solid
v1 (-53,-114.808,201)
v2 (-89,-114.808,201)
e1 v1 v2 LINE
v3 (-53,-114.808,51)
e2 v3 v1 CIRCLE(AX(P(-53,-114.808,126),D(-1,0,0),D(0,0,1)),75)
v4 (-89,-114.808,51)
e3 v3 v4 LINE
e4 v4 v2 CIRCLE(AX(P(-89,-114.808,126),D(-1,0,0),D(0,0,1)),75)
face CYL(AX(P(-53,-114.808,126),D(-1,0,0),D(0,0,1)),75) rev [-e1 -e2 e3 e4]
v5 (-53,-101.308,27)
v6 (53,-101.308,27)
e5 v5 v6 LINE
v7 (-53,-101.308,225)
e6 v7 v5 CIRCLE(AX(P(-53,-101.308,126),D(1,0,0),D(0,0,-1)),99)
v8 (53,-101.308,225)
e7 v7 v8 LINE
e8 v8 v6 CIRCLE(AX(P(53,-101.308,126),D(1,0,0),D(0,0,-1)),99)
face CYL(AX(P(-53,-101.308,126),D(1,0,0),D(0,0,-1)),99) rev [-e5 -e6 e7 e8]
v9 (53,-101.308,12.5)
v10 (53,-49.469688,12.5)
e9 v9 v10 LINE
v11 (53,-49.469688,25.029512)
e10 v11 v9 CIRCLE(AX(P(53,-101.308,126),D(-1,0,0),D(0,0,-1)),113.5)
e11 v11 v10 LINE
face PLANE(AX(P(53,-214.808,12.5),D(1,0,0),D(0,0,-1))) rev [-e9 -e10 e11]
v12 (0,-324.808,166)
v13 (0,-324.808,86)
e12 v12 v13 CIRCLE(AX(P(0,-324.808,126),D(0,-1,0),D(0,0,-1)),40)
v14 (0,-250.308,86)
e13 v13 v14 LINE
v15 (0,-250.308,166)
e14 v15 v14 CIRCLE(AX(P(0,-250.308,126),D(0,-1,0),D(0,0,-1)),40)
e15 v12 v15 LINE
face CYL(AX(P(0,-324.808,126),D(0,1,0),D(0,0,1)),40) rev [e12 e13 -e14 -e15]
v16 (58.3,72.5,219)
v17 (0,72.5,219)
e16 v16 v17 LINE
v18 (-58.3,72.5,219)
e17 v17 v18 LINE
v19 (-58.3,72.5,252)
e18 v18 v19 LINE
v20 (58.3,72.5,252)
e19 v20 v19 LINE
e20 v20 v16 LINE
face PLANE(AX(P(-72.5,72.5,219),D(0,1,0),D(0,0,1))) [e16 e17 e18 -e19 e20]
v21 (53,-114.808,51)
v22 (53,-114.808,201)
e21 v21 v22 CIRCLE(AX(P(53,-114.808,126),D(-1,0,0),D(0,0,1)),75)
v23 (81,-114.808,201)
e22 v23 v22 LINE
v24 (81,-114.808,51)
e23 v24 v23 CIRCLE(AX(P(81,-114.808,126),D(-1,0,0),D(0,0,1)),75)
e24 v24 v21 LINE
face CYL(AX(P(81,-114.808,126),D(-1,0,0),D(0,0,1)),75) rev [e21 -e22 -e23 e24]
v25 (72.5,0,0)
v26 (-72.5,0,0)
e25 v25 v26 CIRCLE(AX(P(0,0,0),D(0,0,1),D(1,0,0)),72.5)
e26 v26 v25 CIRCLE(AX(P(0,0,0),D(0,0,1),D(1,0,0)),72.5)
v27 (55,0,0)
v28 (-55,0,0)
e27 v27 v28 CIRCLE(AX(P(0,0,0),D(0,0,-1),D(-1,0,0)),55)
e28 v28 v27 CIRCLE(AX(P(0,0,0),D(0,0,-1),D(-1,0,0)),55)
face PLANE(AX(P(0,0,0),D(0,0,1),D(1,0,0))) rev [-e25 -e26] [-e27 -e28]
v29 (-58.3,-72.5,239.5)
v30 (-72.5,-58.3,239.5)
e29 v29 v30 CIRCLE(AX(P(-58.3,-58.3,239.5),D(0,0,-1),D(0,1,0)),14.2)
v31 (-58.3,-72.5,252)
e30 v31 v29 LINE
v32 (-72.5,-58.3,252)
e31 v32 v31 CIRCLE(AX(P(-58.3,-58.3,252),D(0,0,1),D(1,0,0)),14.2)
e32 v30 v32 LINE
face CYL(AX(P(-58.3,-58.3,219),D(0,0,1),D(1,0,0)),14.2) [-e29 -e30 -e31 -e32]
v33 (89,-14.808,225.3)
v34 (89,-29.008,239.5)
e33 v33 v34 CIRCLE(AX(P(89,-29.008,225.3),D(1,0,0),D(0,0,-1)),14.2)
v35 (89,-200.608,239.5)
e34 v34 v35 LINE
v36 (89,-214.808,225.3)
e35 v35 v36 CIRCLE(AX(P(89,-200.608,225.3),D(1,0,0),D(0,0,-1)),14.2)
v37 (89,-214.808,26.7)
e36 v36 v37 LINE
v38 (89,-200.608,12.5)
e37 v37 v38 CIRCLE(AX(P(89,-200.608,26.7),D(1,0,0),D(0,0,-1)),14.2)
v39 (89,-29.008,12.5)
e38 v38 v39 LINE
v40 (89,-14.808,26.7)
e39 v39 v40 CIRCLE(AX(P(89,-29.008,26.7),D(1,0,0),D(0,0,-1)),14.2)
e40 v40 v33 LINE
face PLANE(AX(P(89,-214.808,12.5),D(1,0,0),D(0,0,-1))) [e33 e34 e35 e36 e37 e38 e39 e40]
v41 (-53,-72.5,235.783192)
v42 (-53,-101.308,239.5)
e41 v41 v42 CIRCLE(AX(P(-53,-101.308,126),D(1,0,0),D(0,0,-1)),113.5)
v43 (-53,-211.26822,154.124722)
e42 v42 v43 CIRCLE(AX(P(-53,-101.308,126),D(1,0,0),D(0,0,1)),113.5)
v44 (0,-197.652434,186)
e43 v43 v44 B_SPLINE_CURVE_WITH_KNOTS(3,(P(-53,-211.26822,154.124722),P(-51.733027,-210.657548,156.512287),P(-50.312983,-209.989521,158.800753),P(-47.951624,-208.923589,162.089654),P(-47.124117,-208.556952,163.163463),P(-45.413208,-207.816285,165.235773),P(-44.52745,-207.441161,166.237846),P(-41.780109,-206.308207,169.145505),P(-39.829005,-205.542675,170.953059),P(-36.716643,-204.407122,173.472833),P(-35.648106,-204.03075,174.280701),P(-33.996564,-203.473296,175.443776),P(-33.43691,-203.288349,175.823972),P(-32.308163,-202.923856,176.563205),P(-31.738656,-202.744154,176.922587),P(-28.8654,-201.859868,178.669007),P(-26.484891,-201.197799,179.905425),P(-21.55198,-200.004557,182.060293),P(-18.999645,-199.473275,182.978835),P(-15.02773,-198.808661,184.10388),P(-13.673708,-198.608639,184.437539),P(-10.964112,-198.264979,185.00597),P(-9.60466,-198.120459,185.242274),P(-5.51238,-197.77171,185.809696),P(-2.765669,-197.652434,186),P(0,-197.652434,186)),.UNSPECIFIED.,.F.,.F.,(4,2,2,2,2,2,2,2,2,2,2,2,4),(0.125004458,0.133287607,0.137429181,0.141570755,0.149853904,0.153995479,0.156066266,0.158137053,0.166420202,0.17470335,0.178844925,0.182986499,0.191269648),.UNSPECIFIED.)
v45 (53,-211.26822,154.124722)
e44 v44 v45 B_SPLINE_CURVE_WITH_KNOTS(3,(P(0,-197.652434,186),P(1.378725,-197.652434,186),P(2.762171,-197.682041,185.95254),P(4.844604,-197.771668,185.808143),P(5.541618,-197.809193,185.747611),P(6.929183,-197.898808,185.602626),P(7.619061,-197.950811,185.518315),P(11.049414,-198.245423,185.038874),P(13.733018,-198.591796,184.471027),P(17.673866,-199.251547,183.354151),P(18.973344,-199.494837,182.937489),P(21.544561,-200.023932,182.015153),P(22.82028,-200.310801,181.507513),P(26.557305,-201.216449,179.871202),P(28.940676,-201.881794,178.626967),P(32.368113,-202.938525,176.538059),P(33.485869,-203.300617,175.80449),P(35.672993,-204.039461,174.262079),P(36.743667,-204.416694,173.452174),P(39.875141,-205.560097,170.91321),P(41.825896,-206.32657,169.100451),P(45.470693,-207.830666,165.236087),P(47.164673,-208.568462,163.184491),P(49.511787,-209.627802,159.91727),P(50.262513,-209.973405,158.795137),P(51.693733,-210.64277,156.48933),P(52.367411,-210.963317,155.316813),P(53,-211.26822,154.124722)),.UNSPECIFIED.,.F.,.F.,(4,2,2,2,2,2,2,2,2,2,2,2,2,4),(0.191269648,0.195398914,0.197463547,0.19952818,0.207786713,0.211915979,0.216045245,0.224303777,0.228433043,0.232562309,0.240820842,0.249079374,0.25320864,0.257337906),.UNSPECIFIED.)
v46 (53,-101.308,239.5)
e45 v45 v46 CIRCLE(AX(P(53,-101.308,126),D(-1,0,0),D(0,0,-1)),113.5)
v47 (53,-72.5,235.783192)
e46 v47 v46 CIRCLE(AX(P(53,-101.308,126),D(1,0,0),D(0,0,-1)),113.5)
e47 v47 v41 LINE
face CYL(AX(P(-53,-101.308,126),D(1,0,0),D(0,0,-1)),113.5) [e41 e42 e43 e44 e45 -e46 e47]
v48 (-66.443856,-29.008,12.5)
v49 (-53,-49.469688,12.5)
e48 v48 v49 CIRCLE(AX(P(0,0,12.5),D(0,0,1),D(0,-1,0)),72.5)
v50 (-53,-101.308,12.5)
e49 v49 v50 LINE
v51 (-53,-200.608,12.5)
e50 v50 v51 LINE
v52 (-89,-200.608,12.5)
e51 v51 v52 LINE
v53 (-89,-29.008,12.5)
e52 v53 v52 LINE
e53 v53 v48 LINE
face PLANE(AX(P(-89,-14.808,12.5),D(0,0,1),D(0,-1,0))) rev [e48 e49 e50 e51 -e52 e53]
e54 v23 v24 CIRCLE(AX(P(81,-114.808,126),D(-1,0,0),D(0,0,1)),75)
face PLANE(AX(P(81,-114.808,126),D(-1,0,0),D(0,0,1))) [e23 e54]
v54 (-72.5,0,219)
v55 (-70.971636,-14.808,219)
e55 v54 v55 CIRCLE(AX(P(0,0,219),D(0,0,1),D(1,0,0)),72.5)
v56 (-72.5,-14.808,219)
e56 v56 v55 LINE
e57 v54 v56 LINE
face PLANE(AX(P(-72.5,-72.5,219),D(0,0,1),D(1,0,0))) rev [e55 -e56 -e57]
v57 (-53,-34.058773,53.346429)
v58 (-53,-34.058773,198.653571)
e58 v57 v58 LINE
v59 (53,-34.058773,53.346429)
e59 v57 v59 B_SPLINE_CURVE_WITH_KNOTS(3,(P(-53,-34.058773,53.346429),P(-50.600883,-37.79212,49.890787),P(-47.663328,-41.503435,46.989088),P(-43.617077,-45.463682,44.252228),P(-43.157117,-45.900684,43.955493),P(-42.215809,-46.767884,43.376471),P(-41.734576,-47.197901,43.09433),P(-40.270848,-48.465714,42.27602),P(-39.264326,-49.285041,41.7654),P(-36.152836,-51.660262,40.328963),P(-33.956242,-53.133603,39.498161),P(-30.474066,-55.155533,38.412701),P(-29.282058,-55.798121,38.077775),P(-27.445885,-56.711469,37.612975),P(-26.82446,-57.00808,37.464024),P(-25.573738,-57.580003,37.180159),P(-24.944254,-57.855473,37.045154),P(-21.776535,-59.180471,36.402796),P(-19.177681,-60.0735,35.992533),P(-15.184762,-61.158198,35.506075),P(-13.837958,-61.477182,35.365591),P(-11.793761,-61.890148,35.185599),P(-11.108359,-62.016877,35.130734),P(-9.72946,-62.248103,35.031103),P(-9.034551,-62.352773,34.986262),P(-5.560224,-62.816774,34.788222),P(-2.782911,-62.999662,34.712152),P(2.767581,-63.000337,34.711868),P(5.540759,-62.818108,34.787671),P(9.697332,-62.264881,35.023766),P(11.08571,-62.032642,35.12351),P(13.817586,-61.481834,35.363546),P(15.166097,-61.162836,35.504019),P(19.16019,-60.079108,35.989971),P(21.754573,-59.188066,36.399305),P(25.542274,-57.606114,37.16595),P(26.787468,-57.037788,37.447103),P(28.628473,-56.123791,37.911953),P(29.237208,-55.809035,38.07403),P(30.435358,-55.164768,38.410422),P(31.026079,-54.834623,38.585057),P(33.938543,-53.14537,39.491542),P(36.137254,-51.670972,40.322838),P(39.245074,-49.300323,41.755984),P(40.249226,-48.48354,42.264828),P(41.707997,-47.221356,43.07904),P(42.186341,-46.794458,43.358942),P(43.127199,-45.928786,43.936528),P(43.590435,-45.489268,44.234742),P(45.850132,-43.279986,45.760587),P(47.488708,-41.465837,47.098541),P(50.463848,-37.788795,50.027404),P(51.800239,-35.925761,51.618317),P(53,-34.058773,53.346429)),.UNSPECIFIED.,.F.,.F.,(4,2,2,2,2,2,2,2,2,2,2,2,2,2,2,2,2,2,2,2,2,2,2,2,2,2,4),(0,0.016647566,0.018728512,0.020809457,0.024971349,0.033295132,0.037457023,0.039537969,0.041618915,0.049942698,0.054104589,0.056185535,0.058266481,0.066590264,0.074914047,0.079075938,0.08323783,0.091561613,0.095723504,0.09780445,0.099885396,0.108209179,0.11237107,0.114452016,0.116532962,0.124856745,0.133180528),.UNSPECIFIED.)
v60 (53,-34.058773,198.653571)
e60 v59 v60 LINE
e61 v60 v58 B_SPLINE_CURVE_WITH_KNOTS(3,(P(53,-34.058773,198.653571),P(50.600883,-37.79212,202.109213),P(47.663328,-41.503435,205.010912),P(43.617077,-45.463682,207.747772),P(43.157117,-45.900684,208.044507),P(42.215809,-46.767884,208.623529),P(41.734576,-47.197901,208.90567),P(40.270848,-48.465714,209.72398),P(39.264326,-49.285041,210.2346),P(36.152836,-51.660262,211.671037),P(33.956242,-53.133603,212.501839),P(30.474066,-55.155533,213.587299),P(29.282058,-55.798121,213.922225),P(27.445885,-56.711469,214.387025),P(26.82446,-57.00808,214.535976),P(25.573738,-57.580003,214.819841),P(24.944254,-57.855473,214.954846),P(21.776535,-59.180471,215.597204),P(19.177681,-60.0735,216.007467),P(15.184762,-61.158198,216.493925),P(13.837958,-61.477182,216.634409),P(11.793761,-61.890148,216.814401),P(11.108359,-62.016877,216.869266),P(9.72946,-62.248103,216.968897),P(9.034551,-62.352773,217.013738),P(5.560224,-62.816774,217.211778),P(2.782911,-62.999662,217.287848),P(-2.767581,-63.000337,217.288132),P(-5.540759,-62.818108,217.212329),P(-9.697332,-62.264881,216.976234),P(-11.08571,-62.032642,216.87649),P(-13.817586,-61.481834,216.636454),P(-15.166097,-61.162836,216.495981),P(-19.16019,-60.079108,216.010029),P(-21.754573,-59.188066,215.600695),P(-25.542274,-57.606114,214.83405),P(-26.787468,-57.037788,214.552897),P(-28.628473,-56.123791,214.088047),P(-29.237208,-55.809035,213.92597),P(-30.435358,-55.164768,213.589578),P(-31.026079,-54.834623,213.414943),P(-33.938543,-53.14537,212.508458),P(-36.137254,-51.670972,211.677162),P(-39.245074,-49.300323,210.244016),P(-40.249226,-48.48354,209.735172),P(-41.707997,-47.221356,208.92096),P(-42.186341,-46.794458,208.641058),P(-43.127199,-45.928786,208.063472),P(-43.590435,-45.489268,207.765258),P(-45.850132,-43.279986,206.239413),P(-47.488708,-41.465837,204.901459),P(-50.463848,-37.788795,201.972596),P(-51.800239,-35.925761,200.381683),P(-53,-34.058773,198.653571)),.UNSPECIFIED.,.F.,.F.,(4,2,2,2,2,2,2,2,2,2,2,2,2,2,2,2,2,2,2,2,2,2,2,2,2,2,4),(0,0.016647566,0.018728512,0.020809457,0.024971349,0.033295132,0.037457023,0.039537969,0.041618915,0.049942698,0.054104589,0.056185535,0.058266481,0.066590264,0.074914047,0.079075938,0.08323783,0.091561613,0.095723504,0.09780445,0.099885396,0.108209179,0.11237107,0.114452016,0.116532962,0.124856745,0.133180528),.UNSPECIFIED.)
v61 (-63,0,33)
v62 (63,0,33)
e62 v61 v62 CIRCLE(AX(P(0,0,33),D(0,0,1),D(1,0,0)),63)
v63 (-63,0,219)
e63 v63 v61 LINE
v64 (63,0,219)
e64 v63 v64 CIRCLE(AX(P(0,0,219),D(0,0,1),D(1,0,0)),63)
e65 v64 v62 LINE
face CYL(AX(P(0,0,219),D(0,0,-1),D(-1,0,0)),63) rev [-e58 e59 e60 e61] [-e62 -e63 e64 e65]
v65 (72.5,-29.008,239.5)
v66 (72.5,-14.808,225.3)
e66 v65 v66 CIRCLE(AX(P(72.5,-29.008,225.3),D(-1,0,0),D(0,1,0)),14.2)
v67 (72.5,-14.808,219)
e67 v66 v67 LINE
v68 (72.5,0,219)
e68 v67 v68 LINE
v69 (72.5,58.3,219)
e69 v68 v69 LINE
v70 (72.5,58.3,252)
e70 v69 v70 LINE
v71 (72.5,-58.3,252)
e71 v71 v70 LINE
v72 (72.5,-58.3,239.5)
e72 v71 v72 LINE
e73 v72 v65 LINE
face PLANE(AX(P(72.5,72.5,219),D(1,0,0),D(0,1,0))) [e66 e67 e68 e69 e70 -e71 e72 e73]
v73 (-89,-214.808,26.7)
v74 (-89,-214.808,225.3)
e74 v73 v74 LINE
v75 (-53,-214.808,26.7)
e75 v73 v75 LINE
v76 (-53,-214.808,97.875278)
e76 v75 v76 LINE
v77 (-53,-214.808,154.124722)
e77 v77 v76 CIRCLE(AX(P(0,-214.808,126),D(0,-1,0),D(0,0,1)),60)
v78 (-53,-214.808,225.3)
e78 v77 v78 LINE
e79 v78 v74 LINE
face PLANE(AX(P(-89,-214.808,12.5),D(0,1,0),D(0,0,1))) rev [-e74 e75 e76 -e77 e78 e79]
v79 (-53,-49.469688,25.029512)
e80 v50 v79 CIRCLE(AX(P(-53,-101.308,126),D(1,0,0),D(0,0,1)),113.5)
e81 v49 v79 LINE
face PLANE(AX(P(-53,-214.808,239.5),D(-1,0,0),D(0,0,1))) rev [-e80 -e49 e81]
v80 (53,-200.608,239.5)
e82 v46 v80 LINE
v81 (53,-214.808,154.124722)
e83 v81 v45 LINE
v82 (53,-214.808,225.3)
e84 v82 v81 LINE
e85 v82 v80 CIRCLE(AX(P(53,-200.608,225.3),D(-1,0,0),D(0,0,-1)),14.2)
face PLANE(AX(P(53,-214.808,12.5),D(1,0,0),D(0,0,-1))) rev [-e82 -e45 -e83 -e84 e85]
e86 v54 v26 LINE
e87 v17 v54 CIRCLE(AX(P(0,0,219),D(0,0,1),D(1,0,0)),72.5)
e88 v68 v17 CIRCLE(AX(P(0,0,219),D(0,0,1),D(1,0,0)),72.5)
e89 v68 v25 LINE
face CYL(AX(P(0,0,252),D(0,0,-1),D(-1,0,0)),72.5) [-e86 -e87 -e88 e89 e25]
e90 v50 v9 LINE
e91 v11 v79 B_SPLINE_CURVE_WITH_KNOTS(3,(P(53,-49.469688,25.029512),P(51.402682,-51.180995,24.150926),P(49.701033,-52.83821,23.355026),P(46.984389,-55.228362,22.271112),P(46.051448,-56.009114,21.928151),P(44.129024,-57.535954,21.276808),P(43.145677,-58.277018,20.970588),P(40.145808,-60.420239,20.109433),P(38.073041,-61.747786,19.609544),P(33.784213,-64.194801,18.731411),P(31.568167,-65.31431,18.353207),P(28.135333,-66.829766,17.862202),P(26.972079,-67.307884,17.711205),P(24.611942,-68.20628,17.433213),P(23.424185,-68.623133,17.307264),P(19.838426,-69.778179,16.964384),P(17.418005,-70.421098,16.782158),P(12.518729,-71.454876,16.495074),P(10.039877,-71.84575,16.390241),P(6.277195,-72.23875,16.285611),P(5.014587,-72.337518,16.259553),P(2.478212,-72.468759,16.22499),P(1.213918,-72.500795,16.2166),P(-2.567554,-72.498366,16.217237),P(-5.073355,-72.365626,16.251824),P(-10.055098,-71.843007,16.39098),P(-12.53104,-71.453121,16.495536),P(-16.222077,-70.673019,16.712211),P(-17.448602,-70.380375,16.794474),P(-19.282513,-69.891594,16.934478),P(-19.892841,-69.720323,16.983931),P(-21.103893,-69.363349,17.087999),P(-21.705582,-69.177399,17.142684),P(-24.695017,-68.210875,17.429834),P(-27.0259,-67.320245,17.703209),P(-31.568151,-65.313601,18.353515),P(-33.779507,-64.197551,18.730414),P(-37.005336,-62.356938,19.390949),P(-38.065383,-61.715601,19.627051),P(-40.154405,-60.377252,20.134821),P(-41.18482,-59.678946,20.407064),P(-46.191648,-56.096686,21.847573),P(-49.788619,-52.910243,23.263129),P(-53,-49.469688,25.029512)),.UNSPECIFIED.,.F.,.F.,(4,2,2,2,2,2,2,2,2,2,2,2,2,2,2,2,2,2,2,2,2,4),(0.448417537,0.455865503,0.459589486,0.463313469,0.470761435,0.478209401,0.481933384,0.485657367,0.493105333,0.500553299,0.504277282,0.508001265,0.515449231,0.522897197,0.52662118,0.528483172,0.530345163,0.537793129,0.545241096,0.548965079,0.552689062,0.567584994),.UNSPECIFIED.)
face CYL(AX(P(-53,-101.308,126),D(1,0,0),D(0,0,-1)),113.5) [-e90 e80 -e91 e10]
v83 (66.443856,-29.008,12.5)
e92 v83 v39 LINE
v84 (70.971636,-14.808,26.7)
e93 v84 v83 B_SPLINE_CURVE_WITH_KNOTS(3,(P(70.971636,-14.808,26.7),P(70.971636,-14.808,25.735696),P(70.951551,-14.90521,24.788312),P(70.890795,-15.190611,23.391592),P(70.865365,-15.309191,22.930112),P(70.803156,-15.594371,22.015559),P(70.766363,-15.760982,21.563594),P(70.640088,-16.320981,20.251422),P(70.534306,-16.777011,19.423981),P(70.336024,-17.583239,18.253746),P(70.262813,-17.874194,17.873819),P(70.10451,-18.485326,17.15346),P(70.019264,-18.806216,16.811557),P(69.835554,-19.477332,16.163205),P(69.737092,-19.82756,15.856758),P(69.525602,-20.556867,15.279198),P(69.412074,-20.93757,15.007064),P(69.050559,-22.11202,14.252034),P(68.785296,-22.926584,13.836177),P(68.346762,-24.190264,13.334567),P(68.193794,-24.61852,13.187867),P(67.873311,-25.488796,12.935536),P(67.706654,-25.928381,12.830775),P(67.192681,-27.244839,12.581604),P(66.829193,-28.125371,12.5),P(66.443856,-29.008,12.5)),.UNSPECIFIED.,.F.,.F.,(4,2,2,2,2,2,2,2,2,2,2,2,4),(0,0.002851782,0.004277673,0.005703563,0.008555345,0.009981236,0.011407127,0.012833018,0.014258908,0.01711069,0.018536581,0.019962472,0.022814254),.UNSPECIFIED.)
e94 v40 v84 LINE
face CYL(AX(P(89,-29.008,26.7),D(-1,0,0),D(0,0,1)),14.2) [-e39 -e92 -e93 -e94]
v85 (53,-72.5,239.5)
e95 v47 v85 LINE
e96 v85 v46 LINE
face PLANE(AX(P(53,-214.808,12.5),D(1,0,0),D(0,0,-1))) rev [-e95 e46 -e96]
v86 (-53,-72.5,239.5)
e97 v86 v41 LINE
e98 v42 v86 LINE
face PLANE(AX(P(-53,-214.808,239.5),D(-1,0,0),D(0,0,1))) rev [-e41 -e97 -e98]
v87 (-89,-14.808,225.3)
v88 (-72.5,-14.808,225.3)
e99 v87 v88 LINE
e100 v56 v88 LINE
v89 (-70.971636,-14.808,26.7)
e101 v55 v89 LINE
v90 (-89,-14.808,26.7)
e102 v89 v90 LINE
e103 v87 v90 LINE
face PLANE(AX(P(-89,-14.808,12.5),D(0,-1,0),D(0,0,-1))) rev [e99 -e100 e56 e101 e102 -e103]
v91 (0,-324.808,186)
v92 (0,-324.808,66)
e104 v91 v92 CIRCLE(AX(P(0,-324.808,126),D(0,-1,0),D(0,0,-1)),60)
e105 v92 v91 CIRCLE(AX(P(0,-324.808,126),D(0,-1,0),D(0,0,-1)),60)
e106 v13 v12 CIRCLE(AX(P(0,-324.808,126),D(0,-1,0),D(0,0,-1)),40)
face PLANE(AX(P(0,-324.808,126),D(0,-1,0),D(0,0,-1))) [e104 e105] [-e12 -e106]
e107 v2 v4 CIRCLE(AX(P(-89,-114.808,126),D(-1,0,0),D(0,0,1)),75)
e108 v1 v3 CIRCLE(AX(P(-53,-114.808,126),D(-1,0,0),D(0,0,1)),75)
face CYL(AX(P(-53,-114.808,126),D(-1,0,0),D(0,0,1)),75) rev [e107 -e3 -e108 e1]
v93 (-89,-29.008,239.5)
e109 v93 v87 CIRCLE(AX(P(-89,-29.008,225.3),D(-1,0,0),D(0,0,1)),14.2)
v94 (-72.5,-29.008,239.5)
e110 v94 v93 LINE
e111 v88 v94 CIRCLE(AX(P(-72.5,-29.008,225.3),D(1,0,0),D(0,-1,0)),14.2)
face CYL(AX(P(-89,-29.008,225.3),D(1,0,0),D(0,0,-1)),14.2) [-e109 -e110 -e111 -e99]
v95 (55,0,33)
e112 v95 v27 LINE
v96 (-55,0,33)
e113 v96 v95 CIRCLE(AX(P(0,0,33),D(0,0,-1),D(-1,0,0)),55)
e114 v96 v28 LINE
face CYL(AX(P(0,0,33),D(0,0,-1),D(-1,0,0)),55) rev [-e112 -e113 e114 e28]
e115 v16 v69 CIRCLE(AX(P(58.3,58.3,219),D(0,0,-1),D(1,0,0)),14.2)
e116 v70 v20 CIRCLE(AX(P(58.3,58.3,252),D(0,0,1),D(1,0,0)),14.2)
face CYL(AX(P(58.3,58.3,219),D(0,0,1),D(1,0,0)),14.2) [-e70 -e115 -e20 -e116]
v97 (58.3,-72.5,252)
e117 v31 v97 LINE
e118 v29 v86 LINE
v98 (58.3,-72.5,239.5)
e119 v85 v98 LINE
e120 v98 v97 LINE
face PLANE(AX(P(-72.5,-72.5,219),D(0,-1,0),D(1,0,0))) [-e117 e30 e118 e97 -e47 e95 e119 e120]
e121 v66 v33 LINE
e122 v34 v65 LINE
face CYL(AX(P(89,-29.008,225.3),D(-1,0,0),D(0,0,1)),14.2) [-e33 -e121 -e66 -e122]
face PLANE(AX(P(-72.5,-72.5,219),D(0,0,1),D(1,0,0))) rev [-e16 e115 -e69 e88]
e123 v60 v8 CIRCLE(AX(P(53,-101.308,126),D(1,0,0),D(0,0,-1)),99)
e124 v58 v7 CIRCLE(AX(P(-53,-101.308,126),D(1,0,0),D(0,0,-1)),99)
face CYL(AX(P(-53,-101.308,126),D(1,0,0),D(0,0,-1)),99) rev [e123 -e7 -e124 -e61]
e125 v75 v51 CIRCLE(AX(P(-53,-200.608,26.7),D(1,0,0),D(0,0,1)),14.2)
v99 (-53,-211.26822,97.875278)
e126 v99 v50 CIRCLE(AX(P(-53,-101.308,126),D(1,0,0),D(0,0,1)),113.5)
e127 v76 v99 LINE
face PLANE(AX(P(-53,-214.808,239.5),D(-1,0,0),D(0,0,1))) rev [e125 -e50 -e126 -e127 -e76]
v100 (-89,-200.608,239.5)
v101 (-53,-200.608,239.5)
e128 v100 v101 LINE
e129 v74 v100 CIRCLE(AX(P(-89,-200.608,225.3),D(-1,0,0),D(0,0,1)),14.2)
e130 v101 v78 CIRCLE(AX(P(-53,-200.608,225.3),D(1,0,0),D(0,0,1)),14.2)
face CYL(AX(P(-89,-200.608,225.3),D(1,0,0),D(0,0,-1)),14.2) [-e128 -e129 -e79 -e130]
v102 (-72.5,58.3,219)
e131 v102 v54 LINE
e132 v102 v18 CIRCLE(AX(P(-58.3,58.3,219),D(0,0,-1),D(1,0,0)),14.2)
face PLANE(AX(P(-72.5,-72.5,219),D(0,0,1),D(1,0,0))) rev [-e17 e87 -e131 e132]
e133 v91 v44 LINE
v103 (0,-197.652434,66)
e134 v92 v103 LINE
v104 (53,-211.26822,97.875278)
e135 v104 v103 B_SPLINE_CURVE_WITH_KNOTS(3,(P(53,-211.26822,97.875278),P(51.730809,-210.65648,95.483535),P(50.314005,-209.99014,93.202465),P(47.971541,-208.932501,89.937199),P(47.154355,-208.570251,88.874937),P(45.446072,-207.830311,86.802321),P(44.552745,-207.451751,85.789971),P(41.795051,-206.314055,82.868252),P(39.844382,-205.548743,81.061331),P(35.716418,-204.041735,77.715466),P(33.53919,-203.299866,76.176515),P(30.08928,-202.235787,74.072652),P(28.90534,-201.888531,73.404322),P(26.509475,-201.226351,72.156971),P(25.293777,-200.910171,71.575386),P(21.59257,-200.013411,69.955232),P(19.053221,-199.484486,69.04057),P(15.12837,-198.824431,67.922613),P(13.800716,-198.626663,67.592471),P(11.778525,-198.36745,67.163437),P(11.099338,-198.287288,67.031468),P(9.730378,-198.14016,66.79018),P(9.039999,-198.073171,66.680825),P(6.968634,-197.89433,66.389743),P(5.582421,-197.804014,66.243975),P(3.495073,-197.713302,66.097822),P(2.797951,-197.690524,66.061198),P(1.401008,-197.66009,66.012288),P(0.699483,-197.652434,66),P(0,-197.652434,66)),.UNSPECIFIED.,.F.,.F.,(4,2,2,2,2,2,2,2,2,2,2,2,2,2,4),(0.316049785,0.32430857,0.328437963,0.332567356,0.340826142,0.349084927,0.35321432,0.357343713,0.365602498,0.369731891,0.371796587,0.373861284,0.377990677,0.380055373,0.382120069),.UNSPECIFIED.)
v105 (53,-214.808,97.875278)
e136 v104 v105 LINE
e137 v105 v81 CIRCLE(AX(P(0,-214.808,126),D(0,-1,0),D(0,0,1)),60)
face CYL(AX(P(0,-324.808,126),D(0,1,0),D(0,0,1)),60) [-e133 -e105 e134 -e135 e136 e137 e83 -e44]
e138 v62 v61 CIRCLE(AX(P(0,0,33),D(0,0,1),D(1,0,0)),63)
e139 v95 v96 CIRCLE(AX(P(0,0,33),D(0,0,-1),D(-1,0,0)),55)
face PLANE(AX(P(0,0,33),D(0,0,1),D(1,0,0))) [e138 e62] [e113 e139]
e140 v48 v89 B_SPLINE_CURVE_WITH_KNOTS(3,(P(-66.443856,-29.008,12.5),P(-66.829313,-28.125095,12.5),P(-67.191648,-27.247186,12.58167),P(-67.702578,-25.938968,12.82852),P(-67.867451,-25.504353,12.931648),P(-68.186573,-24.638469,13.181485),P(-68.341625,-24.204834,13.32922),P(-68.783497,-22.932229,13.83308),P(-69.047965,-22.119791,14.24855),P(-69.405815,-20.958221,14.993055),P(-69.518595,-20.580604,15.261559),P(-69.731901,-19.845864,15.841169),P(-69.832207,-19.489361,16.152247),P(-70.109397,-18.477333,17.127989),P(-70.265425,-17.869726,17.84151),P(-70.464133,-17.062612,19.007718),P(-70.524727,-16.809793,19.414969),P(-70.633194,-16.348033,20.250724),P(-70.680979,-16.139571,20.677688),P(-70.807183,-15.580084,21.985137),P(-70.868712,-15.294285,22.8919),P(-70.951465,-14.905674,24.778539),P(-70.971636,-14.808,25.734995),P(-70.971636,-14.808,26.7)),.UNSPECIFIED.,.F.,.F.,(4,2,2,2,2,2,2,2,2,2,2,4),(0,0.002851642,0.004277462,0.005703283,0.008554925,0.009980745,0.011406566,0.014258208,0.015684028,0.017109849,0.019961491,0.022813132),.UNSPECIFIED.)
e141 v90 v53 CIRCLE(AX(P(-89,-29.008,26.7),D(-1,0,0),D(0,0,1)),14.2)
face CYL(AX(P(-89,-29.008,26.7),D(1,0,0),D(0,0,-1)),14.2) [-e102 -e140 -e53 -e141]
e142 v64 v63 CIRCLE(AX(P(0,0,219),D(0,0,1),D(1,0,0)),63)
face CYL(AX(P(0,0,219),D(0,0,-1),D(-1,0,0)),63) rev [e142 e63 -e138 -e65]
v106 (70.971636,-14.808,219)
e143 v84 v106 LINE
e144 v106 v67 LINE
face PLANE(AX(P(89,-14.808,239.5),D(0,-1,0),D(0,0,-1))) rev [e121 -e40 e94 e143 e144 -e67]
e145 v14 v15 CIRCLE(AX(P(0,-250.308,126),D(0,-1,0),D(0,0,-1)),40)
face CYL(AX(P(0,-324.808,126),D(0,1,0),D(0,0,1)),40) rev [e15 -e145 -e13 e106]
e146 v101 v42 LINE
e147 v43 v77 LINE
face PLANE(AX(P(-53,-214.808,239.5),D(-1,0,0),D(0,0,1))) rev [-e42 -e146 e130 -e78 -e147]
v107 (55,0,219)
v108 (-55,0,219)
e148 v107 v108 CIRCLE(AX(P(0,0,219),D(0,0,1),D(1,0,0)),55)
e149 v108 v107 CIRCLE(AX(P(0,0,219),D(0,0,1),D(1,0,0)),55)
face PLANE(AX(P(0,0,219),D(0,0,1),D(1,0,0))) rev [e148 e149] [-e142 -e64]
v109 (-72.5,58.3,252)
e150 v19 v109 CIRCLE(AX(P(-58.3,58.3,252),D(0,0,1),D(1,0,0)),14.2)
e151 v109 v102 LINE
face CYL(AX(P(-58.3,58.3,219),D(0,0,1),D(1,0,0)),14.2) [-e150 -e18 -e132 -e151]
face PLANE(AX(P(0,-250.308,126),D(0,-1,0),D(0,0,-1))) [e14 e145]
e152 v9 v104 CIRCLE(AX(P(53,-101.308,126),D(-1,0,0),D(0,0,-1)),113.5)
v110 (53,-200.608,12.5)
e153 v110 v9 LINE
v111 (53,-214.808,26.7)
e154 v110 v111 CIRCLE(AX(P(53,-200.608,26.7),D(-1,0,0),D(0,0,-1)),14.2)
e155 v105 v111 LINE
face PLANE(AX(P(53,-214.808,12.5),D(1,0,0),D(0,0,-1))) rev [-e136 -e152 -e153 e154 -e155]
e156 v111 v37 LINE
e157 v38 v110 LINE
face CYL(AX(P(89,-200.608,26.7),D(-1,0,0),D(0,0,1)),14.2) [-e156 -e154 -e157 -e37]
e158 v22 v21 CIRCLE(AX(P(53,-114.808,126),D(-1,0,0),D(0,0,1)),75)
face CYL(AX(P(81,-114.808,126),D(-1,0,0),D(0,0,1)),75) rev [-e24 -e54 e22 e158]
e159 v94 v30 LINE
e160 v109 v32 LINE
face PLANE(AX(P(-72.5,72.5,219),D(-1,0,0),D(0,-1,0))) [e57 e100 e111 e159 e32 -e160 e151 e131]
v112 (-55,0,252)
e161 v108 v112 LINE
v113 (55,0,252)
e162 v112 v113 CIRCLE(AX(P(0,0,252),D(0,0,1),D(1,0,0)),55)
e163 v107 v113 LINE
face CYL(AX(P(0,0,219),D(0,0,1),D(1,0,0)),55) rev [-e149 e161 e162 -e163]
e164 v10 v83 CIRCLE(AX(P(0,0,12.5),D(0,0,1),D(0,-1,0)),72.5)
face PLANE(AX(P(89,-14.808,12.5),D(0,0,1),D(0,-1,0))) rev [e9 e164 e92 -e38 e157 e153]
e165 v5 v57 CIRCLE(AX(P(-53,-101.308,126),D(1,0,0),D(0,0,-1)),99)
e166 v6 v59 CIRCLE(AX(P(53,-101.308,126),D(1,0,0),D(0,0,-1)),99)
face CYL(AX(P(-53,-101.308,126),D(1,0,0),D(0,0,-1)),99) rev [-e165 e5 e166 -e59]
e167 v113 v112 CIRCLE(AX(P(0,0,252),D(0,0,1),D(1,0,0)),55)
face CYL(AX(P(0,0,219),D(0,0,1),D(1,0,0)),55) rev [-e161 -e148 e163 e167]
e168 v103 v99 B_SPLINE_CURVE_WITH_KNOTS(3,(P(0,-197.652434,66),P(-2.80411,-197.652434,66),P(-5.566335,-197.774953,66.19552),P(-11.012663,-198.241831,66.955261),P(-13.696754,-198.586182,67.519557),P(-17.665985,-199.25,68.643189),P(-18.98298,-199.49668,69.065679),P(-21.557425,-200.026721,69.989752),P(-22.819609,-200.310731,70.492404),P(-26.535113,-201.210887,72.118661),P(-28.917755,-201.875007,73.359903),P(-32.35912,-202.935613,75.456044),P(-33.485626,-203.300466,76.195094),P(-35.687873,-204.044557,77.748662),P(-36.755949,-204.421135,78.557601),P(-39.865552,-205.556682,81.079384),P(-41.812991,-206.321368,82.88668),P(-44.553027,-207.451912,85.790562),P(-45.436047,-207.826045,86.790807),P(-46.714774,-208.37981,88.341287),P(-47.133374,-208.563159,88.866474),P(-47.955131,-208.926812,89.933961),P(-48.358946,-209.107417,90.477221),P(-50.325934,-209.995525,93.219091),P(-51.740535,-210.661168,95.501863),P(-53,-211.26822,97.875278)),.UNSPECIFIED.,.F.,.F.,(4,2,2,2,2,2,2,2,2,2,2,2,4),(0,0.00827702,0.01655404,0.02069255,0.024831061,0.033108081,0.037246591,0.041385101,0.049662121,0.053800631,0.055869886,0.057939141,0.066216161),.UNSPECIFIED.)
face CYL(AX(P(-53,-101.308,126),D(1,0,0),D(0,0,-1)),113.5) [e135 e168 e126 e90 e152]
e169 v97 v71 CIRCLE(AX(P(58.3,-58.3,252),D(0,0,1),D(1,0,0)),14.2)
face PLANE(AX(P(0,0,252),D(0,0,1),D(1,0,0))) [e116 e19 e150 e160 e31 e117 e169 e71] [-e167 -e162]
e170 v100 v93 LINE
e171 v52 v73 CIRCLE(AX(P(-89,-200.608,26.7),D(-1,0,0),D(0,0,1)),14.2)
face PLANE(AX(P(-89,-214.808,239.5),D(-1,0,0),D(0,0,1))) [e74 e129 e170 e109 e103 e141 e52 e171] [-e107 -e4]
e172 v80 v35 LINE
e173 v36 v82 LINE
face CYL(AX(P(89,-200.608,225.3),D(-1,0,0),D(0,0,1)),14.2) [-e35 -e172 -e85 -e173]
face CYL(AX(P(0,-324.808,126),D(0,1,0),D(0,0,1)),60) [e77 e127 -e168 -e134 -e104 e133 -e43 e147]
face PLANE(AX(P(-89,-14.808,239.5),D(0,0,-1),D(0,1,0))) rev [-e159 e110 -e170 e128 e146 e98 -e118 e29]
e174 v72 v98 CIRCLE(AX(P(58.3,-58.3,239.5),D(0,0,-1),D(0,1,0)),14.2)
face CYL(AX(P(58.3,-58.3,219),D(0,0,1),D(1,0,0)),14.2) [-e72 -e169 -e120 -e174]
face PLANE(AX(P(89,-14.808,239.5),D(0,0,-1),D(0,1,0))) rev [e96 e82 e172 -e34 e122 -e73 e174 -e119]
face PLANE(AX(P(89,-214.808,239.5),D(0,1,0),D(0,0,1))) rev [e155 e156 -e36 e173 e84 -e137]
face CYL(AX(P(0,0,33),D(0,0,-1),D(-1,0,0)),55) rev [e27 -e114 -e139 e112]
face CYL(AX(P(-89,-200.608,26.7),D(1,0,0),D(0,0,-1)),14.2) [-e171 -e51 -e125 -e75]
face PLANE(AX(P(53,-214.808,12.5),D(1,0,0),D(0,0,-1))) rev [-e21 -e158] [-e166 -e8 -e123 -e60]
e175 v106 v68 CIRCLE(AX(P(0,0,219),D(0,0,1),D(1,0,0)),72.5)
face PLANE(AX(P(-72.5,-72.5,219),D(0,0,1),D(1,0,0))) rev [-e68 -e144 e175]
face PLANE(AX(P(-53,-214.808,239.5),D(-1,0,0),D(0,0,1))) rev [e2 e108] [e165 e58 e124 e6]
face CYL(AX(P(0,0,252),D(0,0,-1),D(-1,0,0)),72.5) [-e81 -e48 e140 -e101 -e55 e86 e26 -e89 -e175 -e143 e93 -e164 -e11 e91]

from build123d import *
from build123d.topology import SkipClean

# Parameters (mm, degrees)
SKETCH1_R                       = 72.5
BOSS_EXTRUDE1_DEPTH             = 252
SKETCH2_W                       = 145
SKETCH2_H                       = 145
BOSS_EXTRUDE2_DEPTH             = 33
BOSS_EXTRUDE3_DEPTH             = 53
BOSS_EXTRUDE3_DEPTH_BACK        = 53
SKETCH7_R                       = 113.5
SKETCH7_R_2                     = 99
SKETCH8_W                       = 227
SKETCH8_H                       = 200
BOSS_EXTRUDE4_DEPTH             = 36
SKETCH10_W                      = 227
SKETCH10_H                      = 200
BOSS_EXTRUDE5_DEPTH             = 36
SKETCH12_R                      = 75
CUT_EXTRUDE4_DEPTH              = 36
CUT_EXTRUDE1_DEPTH              = 93
CUT_EXTRUDE1_DEPTH_BACK         = 93
SKETCH3_R                       = 63
SKETCH5_R                       = 55
CUT_EXTRUDE3_DEPTH              = 33
SKETCH13_R                      = 75
CUT_EXTRUDE5_DEPTH              = 28
SKETCH15_R                      = 99
CUT_EXTRUDE6_DEPTH              = 106
CUT_EXTRUDE2_START              = -33
SKETCH4_R                       = 55
CUT_EXTRUDE2_DEPTH              = 33
BOSS_EXTRUDE6_REACH             = 394.391
BOSS_EXTRUDE6_END_RADIUS        = 113.5
SKETCH18_R                      = 60
SKETCH18_R_2                    = 40
BOSS_EXTRUDE6_DIRECTION_2_DEPTH = 110
BOSS_EXTRUDE7_START             = -7.282064
SKETCH19_R                      = 40
BOSS_EXTRUDE7_DEPTH             = 42.782064
FILLET1_R                       = 14.2


with BuildPart() as part:
    # Sketch1 → Boss-Extrude1 (new body)
    with BuildSketch(Plane.XY):
        Circle(SKETCH1_R)
    extrude(amount=BOSS_EXTRUDE1_DEPTH)

    # Sketch2 → Boss-Extrude2 (add)
    with BuildSketch(Plane.XY.offset(252)):
        Rectangle(SKETCH2_W, SKETCH2_H)
    extrude(amount=-BOSS_EXTRUDE2_DEPTH)

    # Sketch7 → Boss-Extrude3 (add, two sides: drawn at the far end of the back side and taken through both)
    with BuildSketch(Plane(origin=(0, 0, 0), x_dir=(0, 0, -1), z_dir=(1, 0, 0)).offset(-BOSS_EXTRUDE3_DEPTH_BACK)):
        with Locations((-126, -101.308)):
            Circle(SKETCH7_R)
        with Locations((-126, -101.308)):
            Circle(SKETCH7_R_2, mode=Mode.SUBTRACT)
    extrude(amount=BOSS_EXTRUDE3_DEPTH + BOSS_EXTRUDE3_DEPTH_BACK)

    # Sketch8 → Boss-Extrude4 (add)
    with BuildSketch(Plane(origin=(53, 0, 0), x_dir=(0, 0, -1), z_dir=(1, 0, 0))):
        with Locations((-126, -114.808)):
            Rectangle(SKETCH8_W, SKETCH8_H)
    extrude(amount=BOSS_EXTRUDE4_DEPTH)

    # Sketch10 → Boss-Extrude5 (add)
    with BuildSketch(Plane.ZY.offset(53)):
        with Locations((126, -114.808)):
            Rectangle(SKETCH10_W, SKETCH10_H)
    extrude(amount=BOSS_EXTRUDE5_DEPTH)

    # Sketch12 → Cut-Extrude4 (cut)
    with BuildSketch(Plane.ZY.offset(89)):
        with Locations((126, -114.808)):
            Circle(SKETCH12_R)
    extrude(amount=-CUT_EXTRUDE4_DEPTH, mode=Mode.SUBTRACT)

    # Sketch3 → Cut-Extrude1 (cut, two sides: drawn at the far end of the back side and taken through both)
    with BuildSketch(Plane.XY.offset(126).offset(-CUT_EXTRUDE1_DEPTH_BACK)):
        with Locations(Location((0, 0, 0), (0, 0, 180))):
            Circle(SKETCH3_R)
    extrude(amount=CUT_EXTRUDE1_DEPTH + CUT_EXTRUDE1_DEPTH_BACK, mode=Mode.SUBTRACT)

    # Sketch5 → Cut-Extrude3 (cut)
    with BuildSketch(Plane(origin=(0, 0, 0), x_dir=(-1, 0, 0), z_dir=(0, 0, -1))):
        Circle(SKETCH5_R)
    extrude(amount=-CUT_EXTRUDE3_DEPTH, mode=Mode.SUBTRACT)

    # Sketch13 → Cut-Extrude5 (cut)
    with BuildSketch(Plane.ZY.offset(-53)):
        with Locations((126, -114.808)):
            Circle(SKETCH13_R)
    extrude(amount=-CUT_EXTRUDE5_DEPTH, mode=Mode.SUBTRACT)

    # Sketch15 → Cut-Extrude6 (cut)
    with SkipClean():  # the faces are left unmerged after this step: merging them gives an invalid solid
        with BuildSketch(Plane.ZY.offset(-53)):
            with Locations((126, -101.308)):
                Circle(SKETCH15_R)
        extrude(amount=CUT_EXTRUDE6_DEPTH, mode=Mode.SUBTRACT)

    # Sketch4 → Cut-Extrude2 (cut)
    with SkipClean():  # the faces are left unmerged after this step: merging them gives an invalid solid
        with BuildSketch(Plane.XY.offset(252).offset(CUT_EXTRUDE2_START)):
            with Locations(Location((0, 0, 0), (0, 0, 180))):
                Circle(SKETCH4_R)
        extrude(amount=CUT_EXTRUDE2_DEPTH, mode=Mode.SUBTRACT)

    # Boss-Extrude6: up to this cylinder (the profile starts outside it)
    with SkipClean():  # the faces are left unmerged after this step: merging them gives an invalid solid
        boss_extrude6_end = Plane(origin=(-51.500934, -101.308, 126), z_dir=(1, 0, 0)) * Cylinder(BOSS_EXTRUDE6_END_RADIUS, 1016.782, mode=Mode.PRIVATE)
        # Sketch18 → Boss-Extrude6 (add, up to the surface)
        with BuildSketch(Plane.XZ.offset(214.808), mode=Mode.PRIVATE) as boss_extrude6_sk1:
            with Locations(Location((0, 126, 0), (0, 0, 27.952886589))):
                Circle(SKETCH18_R)
            with Locations(Location((0, 126, 0), (0, 0, 90))):
                Circle(SKETCH18_R_2, mode=Mode.SUBTRACT)
        boss_extrude6_tool1 = extrude(boss_extrude6_sk1.sketch, amount=-BOSS_EXTRUDE6_REACH, mode=Mode.PRIVATE) - boss_extrude6_end
        add(boss_extrude6_tool1.solids().sort_by_distance((-51.500934, -214.808, 98.670765))[0])
        add(boss_extrude6_tool1.solids().sort_by_distance((-51.500934, -214.808, 98.670765))[1])

    # Sketch18 → Boss-Extrude6 direction 2 (add)
    with BuildSketch(Plane.XZ.offset(214.808)):
        with Locations(Location((0, 126, 0), (0, 0, 27.952886589))):
            Circle(SKETCH18_R)
        with Locations(Location((0, 126, 0), (0, 0, 90))):
            Circle(SKETCH18_R_2, mode=Mode.SUBTRACT)
    extrude(amount=BOSS_EXTRUDE6_DIRECTION_2_DEPTH)

    # Sketch19 → Boss-Extrude7 (add)
    with SkipClean():  # the faces are left unmerged after this step: merging them gives an invalid solid
        with BuildSketch(Plane.XZ.offset(214.808).offset(BOSS_EXTRUDE7_START)):
            with Locations(Location((0, 126, 0), (0, 0, 270))):
                Circle(SKETCH19_R)
        extrude(amount=BOSS_EXTRUDE7_DEPTH)

    # Fillet1
    fillet1_edges = [part.edges().sort_by_distance(p)[0] for p in [
        (-72.5, 72.5, 235.5),
        (72.5, 72.5, 235.5),
        (72.5, -72.5, 245.75),
        (79.985818069, -14.808, 12.5),
        (71, -214.808, 12.5),
        (80.75, -14.808, 239.5),
        (71, -214.808, 239.5),
        (-72.5, -72.5, 245.75),
        (-80.75, -14.808, 239.5),
        (-79.985818069, -14.808, 12.5),
        (-71, -214.808, 239.5),
        (-71, -214.808, 12.5),
    ]]
    fillet(fillet1_edges, radius=FILLET1_R)


solid = part.part
